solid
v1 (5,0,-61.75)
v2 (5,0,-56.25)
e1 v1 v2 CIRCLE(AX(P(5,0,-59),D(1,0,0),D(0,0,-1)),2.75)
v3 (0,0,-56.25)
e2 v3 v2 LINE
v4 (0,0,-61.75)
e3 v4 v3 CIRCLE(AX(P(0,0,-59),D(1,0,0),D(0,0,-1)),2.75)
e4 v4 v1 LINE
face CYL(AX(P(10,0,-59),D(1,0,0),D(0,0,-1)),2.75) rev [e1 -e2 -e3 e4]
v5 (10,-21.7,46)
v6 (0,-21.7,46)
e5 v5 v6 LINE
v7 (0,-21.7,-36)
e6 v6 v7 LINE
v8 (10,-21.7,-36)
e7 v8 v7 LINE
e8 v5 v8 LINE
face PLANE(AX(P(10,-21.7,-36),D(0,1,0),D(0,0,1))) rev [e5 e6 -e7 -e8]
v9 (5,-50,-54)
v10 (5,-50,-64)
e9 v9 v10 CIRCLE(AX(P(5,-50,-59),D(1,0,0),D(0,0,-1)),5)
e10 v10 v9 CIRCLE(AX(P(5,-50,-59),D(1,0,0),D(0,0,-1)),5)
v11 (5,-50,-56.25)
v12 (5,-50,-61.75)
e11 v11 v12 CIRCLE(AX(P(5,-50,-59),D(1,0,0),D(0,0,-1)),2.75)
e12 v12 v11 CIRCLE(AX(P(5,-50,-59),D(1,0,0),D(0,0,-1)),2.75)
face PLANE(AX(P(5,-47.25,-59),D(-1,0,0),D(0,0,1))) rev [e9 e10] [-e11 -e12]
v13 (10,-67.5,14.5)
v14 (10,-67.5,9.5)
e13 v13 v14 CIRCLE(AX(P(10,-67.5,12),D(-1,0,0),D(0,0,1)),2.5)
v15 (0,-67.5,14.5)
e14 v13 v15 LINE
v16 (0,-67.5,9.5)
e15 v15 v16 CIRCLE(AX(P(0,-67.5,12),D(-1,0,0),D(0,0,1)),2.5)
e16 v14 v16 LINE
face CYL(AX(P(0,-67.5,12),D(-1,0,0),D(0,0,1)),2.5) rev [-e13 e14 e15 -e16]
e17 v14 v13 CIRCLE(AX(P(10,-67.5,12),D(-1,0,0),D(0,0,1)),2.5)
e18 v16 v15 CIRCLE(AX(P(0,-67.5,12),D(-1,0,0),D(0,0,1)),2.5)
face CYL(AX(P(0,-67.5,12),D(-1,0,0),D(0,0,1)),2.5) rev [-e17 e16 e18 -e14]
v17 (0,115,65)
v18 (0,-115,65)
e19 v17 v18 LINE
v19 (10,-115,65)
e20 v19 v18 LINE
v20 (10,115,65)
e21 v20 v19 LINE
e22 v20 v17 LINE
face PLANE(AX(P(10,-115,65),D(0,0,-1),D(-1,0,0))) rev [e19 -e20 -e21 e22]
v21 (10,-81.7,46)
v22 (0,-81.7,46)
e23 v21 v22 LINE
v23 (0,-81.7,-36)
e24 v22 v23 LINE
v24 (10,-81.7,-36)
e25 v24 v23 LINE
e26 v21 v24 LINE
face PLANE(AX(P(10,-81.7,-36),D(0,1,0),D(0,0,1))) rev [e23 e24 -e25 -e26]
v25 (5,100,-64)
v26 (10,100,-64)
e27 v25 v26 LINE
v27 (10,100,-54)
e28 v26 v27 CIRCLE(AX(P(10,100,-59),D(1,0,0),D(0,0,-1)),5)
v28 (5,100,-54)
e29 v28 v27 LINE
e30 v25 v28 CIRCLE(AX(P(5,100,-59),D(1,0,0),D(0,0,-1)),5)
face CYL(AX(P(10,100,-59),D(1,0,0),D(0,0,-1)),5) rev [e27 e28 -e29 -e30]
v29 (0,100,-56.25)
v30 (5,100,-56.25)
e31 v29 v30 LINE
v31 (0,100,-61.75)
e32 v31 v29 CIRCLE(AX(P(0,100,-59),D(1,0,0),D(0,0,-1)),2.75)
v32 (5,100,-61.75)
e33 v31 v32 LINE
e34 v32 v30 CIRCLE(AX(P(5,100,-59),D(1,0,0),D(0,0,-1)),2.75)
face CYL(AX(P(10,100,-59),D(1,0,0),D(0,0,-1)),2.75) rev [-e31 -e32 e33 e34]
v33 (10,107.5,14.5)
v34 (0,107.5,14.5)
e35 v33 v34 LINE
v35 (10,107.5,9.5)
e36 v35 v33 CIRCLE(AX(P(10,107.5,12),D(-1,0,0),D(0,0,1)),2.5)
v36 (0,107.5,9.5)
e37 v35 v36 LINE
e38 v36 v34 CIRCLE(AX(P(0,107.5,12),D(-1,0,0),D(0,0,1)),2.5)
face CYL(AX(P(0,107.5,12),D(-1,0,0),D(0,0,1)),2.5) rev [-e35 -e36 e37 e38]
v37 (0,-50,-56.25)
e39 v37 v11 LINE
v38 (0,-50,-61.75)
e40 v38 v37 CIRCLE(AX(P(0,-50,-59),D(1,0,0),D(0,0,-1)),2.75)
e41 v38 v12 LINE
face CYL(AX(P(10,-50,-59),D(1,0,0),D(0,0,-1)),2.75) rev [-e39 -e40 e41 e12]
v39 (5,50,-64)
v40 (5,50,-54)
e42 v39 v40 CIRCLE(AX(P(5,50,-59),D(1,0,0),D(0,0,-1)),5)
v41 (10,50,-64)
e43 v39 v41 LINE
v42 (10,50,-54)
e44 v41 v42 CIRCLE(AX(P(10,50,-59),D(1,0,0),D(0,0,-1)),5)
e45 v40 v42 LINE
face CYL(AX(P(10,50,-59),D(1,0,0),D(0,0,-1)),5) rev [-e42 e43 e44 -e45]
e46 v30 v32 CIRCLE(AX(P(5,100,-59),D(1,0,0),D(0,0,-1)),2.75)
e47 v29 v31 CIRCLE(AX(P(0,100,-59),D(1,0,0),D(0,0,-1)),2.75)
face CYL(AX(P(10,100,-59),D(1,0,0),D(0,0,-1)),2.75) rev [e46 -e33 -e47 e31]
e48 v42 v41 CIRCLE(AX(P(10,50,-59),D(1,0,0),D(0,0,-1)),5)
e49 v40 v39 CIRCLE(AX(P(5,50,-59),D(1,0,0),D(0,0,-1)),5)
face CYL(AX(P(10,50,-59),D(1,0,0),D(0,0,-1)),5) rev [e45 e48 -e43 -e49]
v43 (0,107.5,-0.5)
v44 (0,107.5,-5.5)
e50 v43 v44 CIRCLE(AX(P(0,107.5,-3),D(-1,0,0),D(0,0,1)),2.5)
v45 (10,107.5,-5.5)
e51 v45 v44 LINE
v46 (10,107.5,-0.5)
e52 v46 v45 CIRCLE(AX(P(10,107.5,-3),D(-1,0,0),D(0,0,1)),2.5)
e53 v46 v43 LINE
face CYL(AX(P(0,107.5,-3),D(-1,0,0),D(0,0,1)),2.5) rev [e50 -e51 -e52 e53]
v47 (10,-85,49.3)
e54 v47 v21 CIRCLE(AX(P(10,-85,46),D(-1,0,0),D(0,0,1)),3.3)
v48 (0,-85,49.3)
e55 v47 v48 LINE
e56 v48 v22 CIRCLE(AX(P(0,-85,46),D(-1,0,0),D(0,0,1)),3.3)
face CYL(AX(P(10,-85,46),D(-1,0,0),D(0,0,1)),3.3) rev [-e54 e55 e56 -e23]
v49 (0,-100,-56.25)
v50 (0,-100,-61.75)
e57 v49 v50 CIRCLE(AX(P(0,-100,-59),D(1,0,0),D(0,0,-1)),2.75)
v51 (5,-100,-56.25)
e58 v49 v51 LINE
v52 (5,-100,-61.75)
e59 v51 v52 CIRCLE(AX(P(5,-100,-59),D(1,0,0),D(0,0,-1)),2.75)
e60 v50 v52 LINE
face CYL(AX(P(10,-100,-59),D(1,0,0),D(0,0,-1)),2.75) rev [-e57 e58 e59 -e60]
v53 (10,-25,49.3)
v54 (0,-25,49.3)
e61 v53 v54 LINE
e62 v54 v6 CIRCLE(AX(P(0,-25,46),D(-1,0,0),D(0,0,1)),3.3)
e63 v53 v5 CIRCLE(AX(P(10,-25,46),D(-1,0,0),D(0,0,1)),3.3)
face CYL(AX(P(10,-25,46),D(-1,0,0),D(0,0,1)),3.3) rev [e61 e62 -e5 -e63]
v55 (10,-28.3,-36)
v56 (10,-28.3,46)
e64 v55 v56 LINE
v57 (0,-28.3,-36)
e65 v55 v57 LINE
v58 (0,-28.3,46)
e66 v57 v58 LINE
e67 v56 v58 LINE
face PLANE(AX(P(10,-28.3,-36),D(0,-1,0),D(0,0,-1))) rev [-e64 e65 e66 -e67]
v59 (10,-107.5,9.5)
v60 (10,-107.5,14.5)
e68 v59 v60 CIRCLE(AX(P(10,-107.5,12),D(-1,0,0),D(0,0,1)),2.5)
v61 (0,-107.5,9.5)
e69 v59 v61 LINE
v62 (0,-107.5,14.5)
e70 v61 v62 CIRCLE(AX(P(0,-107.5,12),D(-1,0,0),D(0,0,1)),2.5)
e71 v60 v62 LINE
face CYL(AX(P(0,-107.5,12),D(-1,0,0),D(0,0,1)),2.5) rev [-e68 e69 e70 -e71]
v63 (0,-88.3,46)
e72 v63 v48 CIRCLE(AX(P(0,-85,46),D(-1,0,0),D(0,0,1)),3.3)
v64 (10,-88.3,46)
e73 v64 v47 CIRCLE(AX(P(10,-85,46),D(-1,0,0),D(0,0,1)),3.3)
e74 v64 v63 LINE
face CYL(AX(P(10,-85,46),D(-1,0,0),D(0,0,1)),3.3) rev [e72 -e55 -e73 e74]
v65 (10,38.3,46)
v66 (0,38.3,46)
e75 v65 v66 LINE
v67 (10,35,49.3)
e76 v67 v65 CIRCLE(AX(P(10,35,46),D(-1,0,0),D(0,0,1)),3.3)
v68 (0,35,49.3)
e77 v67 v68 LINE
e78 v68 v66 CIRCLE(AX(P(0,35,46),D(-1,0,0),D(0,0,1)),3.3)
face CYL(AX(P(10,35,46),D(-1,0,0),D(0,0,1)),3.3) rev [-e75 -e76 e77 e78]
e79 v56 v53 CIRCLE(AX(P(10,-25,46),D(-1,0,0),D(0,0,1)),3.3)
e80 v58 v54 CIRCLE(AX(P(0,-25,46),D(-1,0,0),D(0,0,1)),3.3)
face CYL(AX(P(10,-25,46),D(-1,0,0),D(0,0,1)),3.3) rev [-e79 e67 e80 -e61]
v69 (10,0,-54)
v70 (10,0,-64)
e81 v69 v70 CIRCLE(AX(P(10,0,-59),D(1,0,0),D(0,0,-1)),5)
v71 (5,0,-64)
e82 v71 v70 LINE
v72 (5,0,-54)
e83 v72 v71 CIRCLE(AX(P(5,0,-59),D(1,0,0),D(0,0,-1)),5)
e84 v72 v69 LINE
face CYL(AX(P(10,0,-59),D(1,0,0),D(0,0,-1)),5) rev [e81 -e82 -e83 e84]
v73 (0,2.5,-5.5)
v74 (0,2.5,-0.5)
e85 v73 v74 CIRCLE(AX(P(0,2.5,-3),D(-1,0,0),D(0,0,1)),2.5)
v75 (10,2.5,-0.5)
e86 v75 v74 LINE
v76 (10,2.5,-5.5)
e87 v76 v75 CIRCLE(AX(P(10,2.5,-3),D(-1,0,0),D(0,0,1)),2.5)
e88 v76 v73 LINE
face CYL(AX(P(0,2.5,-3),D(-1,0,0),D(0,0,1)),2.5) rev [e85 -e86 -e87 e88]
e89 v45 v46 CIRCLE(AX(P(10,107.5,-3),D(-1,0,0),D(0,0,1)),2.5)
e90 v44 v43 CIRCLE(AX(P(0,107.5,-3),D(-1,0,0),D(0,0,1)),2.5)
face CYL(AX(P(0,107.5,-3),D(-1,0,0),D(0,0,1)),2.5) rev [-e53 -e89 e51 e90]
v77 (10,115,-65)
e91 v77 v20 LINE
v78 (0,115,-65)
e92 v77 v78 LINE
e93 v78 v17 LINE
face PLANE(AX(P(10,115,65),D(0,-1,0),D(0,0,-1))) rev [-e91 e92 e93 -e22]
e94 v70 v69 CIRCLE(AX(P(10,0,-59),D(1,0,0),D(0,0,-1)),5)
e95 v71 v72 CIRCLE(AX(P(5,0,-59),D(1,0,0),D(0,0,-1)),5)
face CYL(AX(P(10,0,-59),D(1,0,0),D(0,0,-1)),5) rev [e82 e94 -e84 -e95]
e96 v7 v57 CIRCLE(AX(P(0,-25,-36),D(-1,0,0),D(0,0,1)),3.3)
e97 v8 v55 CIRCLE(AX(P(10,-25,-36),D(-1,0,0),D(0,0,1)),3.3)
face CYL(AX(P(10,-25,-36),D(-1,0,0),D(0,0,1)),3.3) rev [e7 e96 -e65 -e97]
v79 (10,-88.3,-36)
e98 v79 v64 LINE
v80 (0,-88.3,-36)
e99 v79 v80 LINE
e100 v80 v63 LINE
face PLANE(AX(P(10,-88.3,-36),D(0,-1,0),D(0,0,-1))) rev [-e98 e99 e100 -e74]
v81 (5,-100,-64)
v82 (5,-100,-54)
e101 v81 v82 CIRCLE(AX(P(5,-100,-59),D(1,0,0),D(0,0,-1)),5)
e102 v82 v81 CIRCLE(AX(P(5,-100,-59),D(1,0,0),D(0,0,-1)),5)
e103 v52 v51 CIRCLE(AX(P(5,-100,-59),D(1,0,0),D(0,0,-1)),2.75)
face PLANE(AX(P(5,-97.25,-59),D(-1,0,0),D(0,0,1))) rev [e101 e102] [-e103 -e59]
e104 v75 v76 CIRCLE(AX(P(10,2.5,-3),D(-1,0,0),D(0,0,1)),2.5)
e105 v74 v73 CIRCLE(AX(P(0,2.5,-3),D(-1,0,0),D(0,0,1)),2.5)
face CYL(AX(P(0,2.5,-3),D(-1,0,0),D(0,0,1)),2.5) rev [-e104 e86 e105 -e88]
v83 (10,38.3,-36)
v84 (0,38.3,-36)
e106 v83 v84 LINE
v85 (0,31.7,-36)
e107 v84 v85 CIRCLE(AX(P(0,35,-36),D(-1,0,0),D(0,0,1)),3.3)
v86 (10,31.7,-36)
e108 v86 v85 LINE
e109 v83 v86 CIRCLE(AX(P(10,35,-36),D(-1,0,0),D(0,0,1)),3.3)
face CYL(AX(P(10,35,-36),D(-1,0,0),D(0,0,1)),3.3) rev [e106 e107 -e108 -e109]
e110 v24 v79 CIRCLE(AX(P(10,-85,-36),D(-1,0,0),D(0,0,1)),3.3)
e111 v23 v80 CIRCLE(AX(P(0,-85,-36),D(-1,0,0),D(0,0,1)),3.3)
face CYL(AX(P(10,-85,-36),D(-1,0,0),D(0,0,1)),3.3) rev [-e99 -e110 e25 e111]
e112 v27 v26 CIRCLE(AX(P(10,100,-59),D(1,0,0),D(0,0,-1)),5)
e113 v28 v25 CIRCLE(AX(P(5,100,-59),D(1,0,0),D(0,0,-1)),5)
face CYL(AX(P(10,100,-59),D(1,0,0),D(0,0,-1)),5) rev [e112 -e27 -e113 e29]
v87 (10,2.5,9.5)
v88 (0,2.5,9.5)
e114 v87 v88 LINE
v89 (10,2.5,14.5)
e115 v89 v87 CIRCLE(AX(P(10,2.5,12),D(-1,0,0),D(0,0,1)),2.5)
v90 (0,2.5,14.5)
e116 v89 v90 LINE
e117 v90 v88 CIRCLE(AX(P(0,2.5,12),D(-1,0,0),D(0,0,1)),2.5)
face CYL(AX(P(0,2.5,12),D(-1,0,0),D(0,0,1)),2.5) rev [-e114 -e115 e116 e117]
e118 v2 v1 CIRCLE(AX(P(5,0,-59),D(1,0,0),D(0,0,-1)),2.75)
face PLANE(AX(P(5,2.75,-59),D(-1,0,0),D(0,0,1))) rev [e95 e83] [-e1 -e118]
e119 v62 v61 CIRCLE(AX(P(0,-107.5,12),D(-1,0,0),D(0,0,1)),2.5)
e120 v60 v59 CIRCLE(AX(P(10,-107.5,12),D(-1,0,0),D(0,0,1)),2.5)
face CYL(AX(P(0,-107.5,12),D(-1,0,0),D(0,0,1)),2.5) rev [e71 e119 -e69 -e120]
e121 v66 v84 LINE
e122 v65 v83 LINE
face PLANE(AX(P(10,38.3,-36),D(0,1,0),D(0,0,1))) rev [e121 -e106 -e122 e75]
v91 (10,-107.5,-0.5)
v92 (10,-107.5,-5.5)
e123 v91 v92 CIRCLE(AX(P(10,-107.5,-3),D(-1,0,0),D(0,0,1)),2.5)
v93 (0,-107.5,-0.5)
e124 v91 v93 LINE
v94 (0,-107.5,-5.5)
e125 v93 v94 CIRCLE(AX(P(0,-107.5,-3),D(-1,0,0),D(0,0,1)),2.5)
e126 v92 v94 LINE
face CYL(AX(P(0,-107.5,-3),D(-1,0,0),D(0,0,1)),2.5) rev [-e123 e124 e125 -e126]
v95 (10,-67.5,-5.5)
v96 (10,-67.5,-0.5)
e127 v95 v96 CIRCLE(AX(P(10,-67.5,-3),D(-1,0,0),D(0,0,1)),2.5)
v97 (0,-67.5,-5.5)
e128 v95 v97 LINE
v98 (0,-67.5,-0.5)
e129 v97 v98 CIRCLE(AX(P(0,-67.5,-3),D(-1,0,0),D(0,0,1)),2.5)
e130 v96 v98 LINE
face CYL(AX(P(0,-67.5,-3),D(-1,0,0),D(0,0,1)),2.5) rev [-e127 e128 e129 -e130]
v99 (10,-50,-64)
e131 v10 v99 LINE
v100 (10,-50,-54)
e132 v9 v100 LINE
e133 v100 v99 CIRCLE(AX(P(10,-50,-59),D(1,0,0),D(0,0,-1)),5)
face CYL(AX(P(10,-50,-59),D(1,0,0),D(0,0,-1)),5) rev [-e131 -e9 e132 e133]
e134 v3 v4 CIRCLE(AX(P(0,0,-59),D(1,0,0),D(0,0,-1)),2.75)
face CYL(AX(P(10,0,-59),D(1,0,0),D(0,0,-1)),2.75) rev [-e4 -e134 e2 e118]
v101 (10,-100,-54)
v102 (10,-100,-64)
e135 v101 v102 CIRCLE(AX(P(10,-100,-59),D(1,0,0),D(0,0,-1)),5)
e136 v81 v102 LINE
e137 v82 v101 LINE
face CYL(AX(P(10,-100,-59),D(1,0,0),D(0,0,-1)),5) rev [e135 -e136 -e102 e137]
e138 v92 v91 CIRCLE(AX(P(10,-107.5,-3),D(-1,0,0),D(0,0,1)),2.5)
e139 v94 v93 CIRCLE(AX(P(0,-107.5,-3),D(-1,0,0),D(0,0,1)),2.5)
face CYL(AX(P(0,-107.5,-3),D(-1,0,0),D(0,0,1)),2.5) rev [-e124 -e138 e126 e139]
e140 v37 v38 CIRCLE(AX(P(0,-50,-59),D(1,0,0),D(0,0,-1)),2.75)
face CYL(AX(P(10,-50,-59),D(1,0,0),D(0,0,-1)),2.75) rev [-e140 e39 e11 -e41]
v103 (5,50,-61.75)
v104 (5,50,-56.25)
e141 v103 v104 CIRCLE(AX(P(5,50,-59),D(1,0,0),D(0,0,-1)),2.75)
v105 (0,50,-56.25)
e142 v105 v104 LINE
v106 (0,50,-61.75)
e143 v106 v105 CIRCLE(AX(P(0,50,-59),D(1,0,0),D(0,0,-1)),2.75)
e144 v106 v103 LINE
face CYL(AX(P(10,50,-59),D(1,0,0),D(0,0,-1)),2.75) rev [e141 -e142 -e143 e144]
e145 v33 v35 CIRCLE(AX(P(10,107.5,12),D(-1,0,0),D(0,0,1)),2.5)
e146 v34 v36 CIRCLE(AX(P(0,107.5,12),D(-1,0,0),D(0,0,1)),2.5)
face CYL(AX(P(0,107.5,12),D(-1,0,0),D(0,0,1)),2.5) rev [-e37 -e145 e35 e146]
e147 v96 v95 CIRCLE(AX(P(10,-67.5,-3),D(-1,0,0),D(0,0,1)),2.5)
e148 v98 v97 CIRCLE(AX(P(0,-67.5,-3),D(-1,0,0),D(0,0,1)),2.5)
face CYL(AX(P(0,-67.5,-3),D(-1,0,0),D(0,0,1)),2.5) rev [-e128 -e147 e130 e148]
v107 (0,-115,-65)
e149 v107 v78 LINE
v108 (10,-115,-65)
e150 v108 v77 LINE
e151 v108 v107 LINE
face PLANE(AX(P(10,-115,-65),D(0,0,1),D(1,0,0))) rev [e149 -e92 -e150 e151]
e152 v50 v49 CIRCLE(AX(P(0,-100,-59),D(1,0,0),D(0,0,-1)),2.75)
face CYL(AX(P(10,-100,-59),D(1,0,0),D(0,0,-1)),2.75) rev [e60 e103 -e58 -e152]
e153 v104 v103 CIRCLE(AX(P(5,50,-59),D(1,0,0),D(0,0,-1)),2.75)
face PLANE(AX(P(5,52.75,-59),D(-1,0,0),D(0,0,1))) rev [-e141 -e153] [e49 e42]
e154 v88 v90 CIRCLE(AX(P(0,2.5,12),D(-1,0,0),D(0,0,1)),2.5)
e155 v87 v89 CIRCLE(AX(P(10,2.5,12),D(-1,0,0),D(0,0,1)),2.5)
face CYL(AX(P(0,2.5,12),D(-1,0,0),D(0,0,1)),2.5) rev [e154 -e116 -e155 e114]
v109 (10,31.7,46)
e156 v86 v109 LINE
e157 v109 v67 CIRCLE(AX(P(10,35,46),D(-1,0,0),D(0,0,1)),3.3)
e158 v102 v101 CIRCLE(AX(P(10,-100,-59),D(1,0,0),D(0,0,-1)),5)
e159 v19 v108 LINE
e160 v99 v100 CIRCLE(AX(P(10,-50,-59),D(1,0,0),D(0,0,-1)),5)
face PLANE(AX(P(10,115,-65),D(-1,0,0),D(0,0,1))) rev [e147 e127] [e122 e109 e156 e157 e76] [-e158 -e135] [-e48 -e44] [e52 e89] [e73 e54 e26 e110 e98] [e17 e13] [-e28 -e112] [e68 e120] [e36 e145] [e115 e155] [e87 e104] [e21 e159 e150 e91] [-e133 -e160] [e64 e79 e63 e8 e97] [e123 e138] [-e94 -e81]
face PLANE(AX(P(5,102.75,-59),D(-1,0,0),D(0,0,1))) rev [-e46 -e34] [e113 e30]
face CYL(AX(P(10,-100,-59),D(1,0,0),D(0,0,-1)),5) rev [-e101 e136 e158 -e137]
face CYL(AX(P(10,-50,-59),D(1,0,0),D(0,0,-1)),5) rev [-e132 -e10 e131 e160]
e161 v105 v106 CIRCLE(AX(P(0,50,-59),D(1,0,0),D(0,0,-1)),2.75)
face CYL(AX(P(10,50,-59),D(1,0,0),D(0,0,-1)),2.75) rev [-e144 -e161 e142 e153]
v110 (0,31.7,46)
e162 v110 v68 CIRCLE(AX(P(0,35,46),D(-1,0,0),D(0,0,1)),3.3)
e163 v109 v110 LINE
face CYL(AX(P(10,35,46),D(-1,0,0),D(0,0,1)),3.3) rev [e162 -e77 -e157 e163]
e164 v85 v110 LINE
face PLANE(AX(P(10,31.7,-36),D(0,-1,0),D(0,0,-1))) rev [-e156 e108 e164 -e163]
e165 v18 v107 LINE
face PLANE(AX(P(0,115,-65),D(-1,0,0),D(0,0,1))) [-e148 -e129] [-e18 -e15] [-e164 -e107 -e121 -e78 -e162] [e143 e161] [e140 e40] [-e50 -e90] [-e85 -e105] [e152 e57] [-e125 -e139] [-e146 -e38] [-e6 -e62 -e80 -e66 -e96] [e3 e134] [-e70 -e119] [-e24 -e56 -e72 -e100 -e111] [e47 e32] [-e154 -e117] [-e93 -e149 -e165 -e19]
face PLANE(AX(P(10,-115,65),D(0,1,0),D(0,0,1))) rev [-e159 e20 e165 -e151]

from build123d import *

# Parameters (mm, degrees)
SKETCH_1_W                                         = 130
SKETCH_1_H                                         = 230
BOSS_EXTRUDE_1_DEPTH                               = 10
M6_TAPPED_HOLE_1_D                                 = 5
LINEAR_PATTERN_1_COUNT                             = 2
LINEAR_PATTERN_1_PITCH                             = 15
M5_SOCKET_HEAD_CAP_SCREW_COUNTERBORE_1_D           = 5.5
M5_SOCKET_HEAD_CAP_SCREW_COUNTERBORE_1_CBORE_D     = 10
M5_SOCKET_HEAD_CAP_SCREW_COUNTERBORE_1_CBORE_DEPTH = 5
LINEAR_PATTERN_2_COUNT                             = 3
LINEAR_PATTERN_2_PITCH                             = 50
LINEAR_PATTERN_2_COL_COUNT                         = 3
LINEAR_PATTERN_2_COL_PITCH                         = 50
LINEAR_PATTERN_3_COUNT                             = 2
LINEAR_PATTERN_3_PITCH                             = 110
LINEAR_PATTERN_3_COPY_1_D                          = 5
LINEAR_PATTERN_4_COUNT                             = 2
LINEAR_PATTERN_4_PITCH                             = 215
LINEAR_PATTERN_4_COPY_1_D                          = 5
CUT_EXTRUDE_1_DEPTH                                = 133.476412995
LINEAR_PATTERN_8_COUNT                             = 3
LINEAR_PATTERN_8_PITCH                             = 60
LINEAR_PATTERN_7_COUNT                             = 2
LINEAR_PATTERN_7_PITCH                             = 40
LINEAR_PATTERN_7_COPY_1_D                          = 5


with BuildPart() as part:
    # Sketch 1 → Boss-Extrude 1 (new body)
    with BuildSketch(Plane(origin=(0, 0, 0), x_dir=(0, 0, -1), z_dir=(1, 0, 0))):
        Rectangle(SKETCH_1_W, SKETCH_1_H)
    extrude(amount=BOSS_EXTRUDE_1_DEPTH)

    # M6 Tapped Hole 1 (through all)
    with Locations(Plane.ZY):
        with Locations((12, -107.5)):
            m6_tapped_hole_1 = Hole(M6_TAPPED_HOLE_1_D / 2)

    # Linear Pattern 1: M6 Tapped Hole 1 ×2
    with Locations(*[(0, 0, -i * LINEAR_PATTERN_1_PITCH) for i in range(1, LINEAR_PATTERN_1_COUNT)]):
        add(m6_tapped_hole_1, mode=Mode.SUBTRACT)

    # M5 Socket Head Cap Screw Counterbore 1 (through all)
    with Locations(Plane(origin=(10, 0, 0), x_dir=(0, 0, -1), z_dir=(1, 0, 0))):
        with Locations((59, 0)):
            m5_socket_head_cap_screw_counterbore_1 = CounterBoreHole(M5_SOCKET_HEAD_CAP_SCREW_COUNTERBORE_1_D / 2, M5_SOCKET_HEAD_CAP_SCREW_COUNTERBORE_1_CBORE_D / 2, M5_SOCKET_HEAD_CAP_SCREW_COUNTERBORE_1_CBORE_DEPTH)

    # Linear Pattern 2: M5 Socket Head Cap Screw Counterbore 1 ×3
    with Locations(*[(0, i * LINEAR_PATTERN_2_PITCH, 0) for i in range(1, LINEAR_PATTERN_2_COUNT)]):
        add(m5_socket_head_cap_screw_counterbore_1, mode=Mode.SUBTRACT)

    # Linear Pattern 2 col: M5 Socket Head Cap Screw Counterbore 1 ×3
    with Locations(*[(0, -i * LINEAR_PATTERN_2_COL_PITCH, 0) for i in range(1, LINEAR_PATTERN_2_COL_COUNT)]):
        add(m5_socket_head_cap_screw_counterbore_1, mode=Mode.SUBTRACT)

    # Linear Pattern 3: M6 Tapped Hole 1 ×2
    with Locations(*[(0, i * LINEAR_PATTERN_3_PITCH, 0) for i in range(1, LINEAR_PATTERN_3_COUNT)]):
        add(m6_tapped_hole_1, mode=Mode.SUBTRACT)

    # Linear Pattern 3 copy 1 (through all)
    with Locations(Plane(origin=(0, 110, -15), x_dir=(0, 0, 1), z_dir=(-1, 0, 0))):
        with Locations((12, -107.5)):
            Hole(LINEAR_PATTERN_3_COPY_1_D / 2)

    # Linear Pattern 4: M6 Tapped Hole 1 ×2
    with Locations(*[(0, i * LINEAR_PATTERN_4_PITCH, 0) for i in range(1, LINEAR_PATTERN_4_COUNT)]):
        add(m6_tapped_hole_1, mode=Mode.SUBTRACT)

    # Linear Pattern 4 copy 1 (through all)
    with Locations(Plane(origin=(0, 215, -15), x_dir=(0, 0, 1), z_dir=(-1, 0, 0))):
        with Locations((12, -107.5)):
            Hole(LINEAR_PATTERN_4_COPY_1_D / 2)

    # Sketch 8 → Cut-Extrude 1 (cut, through all)
    with BuildSketch(Plane.ZY):
        with BuildLine():
            Line((-36, -81.7), (46, -81.7))
            ThreePointArc((46, -81.7), (49.3, -85), (46, -88.3))
            Line((46, -88.3), (-36, -88.3))
            ThreePointArc((-36, -88.3), (-39.3, -85), (-36, -81.7))
        make_face()
    cut_extrude_1 = extrude(amount=-CUT_EXTRUDE_1_DEPTH, mode=Mode.SUBTRACT)

    # Linear Pattern 8: Cut-Extrude 1 ×3
    with Locations(*[(0, i * LINEAR_PATTERN_8_PITCH, 0) for i in range(1, LINEAR_PATTERN_8_COUNT)]):
        add(cut_extrude_1, mode=Mode.SUBTRACT)

    # Linear Pattern 7: M6 Tapped Hole 1 ×2
    with Locations(*[(0, i * LINEAR_PATTERN_7_PITCH, 0) for i in range(1, LINEAR_PATTERN_7_COUNT)]):
        add(m6_tapped_hole_1, mode=Mode.SUBTRACT)

    # Linear Pattern 7 copy 1 (through all)
    with Locations(Plane(origin=(0, 40, -15), x_dir=(0, 0, 1), z_dir=(-1, 0, 0))):
        with Locations((12, -107.5)):
            Hole(LINEAR_PATTERN_7_COPY_1_D / 2)


solid = part.part
